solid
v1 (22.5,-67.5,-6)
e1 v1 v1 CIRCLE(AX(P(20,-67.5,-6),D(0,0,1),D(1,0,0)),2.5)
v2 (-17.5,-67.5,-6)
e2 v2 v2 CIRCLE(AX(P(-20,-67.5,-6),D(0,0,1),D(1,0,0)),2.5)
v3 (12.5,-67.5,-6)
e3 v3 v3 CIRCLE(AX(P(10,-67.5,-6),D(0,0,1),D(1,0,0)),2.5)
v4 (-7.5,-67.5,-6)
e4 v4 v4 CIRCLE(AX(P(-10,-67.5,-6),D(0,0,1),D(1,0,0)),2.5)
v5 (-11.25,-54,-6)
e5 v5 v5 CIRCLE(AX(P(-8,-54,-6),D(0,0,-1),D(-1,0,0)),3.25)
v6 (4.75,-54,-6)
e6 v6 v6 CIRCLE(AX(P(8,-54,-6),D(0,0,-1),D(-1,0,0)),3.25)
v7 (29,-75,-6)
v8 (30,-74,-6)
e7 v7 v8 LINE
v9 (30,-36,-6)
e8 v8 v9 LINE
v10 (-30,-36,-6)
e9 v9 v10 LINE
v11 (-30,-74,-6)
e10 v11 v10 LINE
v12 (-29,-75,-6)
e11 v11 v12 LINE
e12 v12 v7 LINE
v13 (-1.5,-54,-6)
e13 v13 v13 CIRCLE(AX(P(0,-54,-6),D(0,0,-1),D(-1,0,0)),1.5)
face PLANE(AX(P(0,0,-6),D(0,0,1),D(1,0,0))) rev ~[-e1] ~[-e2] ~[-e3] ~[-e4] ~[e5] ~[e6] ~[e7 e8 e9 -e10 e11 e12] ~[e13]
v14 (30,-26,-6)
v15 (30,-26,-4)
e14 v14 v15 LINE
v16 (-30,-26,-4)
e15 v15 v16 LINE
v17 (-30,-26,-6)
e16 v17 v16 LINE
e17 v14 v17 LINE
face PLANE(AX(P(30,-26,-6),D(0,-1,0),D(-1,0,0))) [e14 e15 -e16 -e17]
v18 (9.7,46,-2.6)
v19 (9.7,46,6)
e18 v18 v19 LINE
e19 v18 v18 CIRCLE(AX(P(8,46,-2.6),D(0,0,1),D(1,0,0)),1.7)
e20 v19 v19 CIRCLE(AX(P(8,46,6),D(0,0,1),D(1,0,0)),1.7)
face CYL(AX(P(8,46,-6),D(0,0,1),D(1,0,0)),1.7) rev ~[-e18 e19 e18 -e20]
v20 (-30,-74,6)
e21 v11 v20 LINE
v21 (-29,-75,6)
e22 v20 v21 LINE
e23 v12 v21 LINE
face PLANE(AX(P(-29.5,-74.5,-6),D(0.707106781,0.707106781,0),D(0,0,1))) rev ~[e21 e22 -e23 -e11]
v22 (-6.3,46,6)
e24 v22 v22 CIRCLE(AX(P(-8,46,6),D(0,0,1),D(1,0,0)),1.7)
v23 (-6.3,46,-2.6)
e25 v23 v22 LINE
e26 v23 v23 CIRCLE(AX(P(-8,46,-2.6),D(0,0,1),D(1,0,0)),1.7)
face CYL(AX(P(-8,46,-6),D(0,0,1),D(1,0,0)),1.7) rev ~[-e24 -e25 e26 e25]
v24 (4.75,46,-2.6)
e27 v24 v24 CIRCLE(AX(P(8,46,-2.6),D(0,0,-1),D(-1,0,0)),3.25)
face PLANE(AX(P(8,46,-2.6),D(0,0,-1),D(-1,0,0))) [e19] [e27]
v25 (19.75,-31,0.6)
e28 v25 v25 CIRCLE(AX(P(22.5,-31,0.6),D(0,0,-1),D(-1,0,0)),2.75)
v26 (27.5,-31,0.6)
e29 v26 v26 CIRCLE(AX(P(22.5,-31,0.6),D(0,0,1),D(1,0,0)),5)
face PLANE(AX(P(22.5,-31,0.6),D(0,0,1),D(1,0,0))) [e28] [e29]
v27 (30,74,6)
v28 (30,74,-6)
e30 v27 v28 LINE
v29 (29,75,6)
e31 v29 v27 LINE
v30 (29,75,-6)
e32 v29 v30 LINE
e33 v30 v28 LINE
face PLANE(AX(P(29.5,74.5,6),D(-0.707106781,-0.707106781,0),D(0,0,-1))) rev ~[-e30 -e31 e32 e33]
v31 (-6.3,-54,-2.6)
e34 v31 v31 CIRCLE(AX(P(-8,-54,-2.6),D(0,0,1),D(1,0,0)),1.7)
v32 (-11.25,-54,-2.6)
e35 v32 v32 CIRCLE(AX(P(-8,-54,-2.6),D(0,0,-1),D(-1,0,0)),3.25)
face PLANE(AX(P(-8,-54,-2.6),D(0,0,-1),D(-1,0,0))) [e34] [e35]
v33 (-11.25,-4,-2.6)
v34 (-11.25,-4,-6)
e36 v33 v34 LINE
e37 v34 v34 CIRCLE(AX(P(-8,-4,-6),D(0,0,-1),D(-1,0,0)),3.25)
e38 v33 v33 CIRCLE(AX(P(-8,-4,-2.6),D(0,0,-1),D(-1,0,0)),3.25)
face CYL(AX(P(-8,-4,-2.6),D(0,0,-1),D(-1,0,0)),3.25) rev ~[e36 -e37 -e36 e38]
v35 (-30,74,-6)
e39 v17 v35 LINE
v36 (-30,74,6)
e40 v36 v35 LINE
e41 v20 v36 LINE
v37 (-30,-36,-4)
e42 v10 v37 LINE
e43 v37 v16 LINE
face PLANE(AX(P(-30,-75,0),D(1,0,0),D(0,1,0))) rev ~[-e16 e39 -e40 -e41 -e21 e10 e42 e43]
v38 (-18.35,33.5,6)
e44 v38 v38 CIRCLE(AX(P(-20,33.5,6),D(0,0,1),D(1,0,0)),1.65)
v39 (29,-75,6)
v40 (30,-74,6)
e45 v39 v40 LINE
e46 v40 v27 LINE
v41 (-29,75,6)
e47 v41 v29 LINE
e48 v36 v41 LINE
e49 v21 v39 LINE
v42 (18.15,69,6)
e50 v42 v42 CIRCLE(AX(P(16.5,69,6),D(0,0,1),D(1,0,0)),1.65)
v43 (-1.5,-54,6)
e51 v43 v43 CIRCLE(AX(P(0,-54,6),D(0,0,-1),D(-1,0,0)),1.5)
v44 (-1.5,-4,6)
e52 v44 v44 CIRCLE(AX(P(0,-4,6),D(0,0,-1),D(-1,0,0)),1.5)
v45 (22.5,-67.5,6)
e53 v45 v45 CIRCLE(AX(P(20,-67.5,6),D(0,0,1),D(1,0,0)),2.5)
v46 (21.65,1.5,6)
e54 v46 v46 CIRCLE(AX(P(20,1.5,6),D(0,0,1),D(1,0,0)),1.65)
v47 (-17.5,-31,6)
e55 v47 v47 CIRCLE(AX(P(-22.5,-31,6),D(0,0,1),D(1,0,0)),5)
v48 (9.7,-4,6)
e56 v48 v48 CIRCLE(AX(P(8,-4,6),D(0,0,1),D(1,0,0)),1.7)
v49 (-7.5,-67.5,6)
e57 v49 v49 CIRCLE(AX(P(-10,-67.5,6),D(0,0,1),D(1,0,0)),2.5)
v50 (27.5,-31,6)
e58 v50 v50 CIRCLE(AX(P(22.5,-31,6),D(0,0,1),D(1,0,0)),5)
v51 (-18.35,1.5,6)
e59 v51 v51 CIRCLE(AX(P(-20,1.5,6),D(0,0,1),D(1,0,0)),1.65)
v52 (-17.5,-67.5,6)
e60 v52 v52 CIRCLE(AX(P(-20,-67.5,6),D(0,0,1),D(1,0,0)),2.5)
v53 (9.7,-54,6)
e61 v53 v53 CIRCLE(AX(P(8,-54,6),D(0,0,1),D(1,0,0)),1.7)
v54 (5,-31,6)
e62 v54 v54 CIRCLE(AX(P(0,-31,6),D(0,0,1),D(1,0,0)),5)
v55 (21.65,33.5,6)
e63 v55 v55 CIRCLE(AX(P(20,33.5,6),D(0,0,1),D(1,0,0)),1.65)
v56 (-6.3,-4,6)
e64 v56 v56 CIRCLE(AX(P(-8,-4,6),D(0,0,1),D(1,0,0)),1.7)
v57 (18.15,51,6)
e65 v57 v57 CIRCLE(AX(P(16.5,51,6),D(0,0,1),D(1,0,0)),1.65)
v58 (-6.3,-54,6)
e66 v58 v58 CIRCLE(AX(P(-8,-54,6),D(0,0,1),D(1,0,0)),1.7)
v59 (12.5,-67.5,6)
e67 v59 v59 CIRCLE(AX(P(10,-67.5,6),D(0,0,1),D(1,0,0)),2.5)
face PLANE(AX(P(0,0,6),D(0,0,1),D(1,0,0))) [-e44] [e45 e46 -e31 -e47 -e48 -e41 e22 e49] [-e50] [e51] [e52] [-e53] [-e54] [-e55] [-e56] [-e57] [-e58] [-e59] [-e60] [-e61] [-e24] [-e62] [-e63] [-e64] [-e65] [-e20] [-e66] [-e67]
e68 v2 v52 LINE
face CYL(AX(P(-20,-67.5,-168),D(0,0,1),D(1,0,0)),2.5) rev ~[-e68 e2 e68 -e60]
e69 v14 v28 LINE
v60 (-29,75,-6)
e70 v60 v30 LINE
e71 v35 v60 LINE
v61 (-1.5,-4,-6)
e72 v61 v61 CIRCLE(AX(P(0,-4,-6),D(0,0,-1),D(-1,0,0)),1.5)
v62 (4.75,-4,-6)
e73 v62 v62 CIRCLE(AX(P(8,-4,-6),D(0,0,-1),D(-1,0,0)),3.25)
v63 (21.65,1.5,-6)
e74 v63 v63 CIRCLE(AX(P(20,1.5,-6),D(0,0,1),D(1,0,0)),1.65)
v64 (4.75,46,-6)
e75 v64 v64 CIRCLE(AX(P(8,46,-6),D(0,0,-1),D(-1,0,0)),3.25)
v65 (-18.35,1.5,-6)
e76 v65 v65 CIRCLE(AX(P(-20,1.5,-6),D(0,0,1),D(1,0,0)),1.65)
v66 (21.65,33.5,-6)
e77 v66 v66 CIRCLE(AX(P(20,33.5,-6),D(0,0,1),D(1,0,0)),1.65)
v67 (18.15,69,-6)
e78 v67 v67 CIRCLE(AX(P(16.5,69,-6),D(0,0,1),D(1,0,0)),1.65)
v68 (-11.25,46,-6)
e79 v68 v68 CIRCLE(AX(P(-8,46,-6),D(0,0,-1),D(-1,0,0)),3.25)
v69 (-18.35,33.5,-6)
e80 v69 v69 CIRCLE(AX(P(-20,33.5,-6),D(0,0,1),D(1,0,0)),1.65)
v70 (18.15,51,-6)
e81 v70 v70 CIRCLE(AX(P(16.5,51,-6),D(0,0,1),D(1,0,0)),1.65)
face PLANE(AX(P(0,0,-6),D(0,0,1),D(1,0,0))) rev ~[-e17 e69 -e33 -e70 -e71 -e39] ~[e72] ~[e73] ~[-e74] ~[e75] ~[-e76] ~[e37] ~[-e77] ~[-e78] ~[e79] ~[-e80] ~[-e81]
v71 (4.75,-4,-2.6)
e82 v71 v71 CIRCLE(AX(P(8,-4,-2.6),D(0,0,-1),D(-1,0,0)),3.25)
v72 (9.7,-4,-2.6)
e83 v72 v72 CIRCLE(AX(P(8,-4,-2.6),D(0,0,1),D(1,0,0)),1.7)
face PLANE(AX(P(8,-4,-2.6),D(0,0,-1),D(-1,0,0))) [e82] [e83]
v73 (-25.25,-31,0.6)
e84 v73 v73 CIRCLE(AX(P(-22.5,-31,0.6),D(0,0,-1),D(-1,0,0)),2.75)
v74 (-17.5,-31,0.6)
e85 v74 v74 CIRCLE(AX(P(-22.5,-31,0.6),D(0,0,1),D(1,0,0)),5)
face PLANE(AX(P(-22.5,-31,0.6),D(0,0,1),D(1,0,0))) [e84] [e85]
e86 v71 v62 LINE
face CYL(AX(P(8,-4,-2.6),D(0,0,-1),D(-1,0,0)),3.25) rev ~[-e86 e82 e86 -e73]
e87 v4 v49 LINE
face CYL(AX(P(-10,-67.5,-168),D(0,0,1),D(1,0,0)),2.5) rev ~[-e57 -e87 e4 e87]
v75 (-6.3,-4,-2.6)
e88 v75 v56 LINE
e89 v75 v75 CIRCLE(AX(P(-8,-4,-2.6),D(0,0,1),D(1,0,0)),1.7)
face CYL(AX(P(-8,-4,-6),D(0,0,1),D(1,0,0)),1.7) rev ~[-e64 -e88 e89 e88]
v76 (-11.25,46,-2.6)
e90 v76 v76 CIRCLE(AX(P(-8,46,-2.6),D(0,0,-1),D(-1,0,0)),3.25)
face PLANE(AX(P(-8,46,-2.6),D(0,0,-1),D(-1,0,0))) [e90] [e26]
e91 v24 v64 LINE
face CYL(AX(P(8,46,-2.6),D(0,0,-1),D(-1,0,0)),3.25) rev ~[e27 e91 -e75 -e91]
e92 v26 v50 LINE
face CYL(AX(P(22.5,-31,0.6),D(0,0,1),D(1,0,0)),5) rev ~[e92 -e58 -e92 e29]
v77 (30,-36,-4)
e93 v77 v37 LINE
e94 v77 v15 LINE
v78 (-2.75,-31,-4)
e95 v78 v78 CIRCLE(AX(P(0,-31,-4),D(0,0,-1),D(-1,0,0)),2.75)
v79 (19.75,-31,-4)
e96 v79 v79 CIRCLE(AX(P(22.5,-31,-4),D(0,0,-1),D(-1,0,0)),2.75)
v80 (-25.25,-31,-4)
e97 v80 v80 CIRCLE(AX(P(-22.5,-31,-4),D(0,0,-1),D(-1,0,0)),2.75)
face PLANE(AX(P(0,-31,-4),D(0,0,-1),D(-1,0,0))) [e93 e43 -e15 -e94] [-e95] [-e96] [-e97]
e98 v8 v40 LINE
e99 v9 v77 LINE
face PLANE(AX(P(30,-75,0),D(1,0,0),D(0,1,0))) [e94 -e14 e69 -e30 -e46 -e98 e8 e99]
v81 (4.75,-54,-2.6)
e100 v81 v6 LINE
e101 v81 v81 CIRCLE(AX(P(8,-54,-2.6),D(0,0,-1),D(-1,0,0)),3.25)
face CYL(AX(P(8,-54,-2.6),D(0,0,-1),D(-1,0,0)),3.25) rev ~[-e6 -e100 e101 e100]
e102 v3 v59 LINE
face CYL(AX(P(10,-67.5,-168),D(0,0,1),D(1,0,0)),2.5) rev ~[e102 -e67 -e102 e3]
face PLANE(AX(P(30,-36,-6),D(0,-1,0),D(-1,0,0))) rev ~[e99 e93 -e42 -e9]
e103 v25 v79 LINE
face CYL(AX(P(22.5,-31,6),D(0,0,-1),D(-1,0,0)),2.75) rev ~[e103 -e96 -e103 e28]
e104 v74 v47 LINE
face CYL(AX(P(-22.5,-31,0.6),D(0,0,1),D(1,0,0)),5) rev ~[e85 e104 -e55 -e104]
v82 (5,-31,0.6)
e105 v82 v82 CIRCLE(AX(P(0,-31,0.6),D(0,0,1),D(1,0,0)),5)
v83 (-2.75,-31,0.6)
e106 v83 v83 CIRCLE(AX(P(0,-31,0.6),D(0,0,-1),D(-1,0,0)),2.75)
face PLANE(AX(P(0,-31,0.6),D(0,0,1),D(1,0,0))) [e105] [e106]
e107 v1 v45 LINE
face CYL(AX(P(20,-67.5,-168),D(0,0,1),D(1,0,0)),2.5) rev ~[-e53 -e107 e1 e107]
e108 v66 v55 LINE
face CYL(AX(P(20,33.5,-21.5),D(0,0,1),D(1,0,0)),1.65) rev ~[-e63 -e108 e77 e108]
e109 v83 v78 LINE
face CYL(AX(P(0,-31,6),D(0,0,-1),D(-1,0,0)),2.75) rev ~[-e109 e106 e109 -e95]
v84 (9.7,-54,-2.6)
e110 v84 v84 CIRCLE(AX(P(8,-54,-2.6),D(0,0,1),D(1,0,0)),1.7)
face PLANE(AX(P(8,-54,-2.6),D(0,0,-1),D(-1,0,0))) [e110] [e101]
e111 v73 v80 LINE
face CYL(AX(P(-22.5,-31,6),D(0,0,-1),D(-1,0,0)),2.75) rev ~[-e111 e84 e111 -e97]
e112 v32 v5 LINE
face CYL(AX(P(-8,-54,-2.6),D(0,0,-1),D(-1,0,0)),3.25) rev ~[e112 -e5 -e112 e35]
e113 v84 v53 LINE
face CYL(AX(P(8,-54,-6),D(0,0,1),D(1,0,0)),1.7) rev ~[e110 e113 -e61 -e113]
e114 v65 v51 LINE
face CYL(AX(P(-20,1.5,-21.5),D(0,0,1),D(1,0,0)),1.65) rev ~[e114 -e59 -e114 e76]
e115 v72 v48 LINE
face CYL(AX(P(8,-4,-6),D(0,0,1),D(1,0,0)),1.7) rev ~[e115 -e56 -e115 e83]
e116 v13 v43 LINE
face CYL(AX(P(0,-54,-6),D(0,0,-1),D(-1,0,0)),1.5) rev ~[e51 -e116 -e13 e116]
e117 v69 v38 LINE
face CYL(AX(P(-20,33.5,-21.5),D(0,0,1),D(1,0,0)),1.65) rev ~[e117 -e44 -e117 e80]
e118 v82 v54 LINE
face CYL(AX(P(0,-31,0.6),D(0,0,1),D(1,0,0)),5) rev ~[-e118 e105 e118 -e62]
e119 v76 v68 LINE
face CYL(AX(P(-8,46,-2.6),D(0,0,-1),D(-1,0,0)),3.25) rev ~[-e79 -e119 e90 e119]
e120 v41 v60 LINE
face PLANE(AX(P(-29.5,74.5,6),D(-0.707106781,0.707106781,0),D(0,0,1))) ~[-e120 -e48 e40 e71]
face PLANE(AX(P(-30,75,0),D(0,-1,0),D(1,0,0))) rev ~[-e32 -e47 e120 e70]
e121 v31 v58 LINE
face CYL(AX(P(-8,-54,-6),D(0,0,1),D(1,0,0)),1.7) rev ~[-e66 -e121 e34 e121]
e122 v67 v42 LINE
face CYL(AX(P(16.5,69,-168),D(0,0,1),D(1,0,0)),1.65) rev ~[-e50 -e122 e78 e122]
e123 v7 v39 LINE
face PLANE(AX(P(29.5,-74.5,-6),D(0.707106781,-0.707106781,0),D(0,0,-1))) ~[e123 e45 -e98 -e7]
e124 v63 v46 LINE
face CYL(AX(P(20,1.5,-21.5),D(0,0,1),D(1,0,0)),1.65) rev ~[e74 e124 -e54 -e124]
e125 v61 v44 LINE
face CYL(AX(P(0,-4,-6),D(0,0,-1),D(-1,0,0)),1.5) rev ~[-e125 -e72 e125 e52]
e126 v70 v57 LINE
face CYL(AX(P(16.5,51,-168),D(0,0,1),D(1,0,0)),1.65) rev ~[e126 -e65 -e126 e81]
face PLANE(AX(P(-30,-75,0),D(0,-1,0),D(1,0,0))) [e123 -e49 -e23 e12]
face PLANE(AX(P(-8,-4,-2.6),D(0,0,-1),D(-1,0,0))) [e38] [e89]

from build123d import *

# Parameters (mm, degrees)
SKETCH1_W                                           = 60
SKETCH1_H                                           = 150
BOSS_EXTRUDE1_DEPTH                                 = 6
M4_TAPPED_HOLE1_D                                   = 3.3
M4_TAPPED_HOLE2_D                                   = 3.3
M4_TAPPED_HOLE2_DEPTH                               = 15.5
M4_TAPPED_HOLE2_TIP                                 = 0.991420021
M6_TAPPED_HOLE2_D                                   = 5
BLIND_PIN_HOLE2_SIZE_MM_D                           = 5
CHAMFER1_SIZE                                       = 1
CBORE_FOR_M3_HEX_SOCKET_HEAD_CAP_SCREW1_D           = 3.4
CBORE_FOR_M3_HEX_SOCKET_HEAD_CAP_SCREW1_CBORE_D     = 6.5
CBORE_FOR_M3_HEX_SOCKET_HEAD_CAP_SCREW1_CBORE_DEPTH = 3.4
LPATTERN1_COUNT                                     = 3
LPATTERN1_PITCH                                     = 50
SKETCH20_R                                          = 1.5
CUT_EXTRUDE1_DEPTH                                  = 82.663945533
SKETCH21_W                                          = 60
SKETCH21_H                                          = 10
CUT_EXTRUDE2_DEPTH                                  = 2
CBORE_FOR_M5_HEX_SOCKET_HEAD_CAP_SCREW1_D           = 5.5
CBORE_FOR_M5_HEX_SOCKET_HEAD_CAP_SCREW1_CBORE_D     = 10
CBORE_FOR_M5_HEX_SOCKET_HEAD_CAP_SCREW1_CBORE_DEPTH = 5.4


with BuildPart() as part:
    # Sketch1 → Boss-Extrude1 (new, symmetric)
    with BuildSketch(Plane.XY):
        Rectangle(SKETCH1_W, SKETCH1_H)
    extrude(amount=BOSS_EXTRUDE1_DEPTH, both=True)

    # M4 Tapped Hole1 (through all)
    with Locations(Plane(origin=(0, 0, -6), x_dir=(-1, 0, 0), z_dir=(0, 0, -1))):
        with Locations((-16.5, 69), (-16.5, 51)):
            Hole(M4_TAPPED_HOLE1_D / 2)

    # M4 Tapped Hole2
    with Locations(Plane(origin=(0, 0, -6), x_dir=(-1, 0, 0), z_dir=(0, 0, -1))):
        with Locations((-20, 33.5), (-20, 1.5), (20, 33.5), (20, 1.5)):
            Hole(M4_TAPPED_HOLE2_D / 2, depth=M4_TAPPED_HOLE2_DEPTH)
            with Locations((0, 0, -(M4_TAPPED_HOLE2_DEPTH + M4_TAPPED_HOLE2_TIP / 2))):  # 118° drill point
                Cone(0, M4_TAPPED_HOLE2_D / 2, M4_TAPPED_HOLE2_TIP, mode=Mode.SUBTRACT)

    # M6 Tapped Hole2 (through all)
    with Locations(Plane(origin=(0, 0, -6), x_dir=(-1, 0, 0), z_dir=(0, 0, -1))):
        with Locations((20, -67.5), (-20, -67.5)):
            Hole(M6_TAPPED_HOLE2_D / 2)

    # Blind Pin Hole2 size mm (through all)
    with Locations(Plane(origin=(0, 0, -6), x_dir=(-1, 0, 0), z_dir=(0, 0, -1))):
        with Locations((10, -67.5), (-10, -67.5)):
            Hole(BLIND_PIN_HOLE2_SIZE_MM_D / 2)

    # Chamfer1
    chamfer1_edges = [part.edges().sort_by_distance(p)[0] for p in [
        (30, -75, 0),
        (-30, -75, 0),
        (-30, 75, 0),
        (30, 75, 0),
    ]]
    chamfer(chamfer1_edges, length=CHAMFER1_SIZE)

    # CBORE for M3 Hex Socket Head Cap Screw1 (through all)
    with Locations(Plane(origin=(0, 0, -6), x_dir=(-1, 0, 0), z_dir=(0, 0, -1))):
        with Locations((8, -54), (-8, -54)):
            cbore_for_m3_hex_socket_head_cap_screw1 = CounterBoreHole(CBORE_FOR_M3_HEX_SOCKET_HEAD_CAP_SCREW1_D / 2, CBORE_FOR_M3_HEX_SOCKET_HEAD_CAP_SCREW1_CBORE_D / 2, CBORE_FOR_M3_HEX_SOCKET_HEAD_CAP_SCREW1_CBORE_DEPTH)

    # LPattern1: CBORE for M3 Hex Socket Head Cap Screw1 ×3
    with Locations(*[(0, i * LPATTERN1_PITCH, 0) for i in range(1, LPATTERN1_COUNT)]):
        add(cbore_for_m3_hex_socket_head_cap_screw1, mode=Mode.SUBTRACT)

    # Sketch20 → Cut-Extrude1 (cut, through all)
    with BuildSketch(Plane(origin=(0, 0, -6), x_dir=(-1, 0, 0), z_dir=(0, 0, -1))):
        with Locations((0, -4)):
            Circle(SKETCH20_R)
        with Locations((0, -54)):
            Circle(SKETCH20_R)
    extrude(amount=-CUT_EXTRUDE1_DEPTH, mode=Mode.SUBTRACT)

    # Sketch21 → Cut-Extrude2 (cut)
    with BuildSketch(Plane(origin=(0, 0, -6), x_dir=(-1, 0, 0), z_dir=(0, 0, -1))):
        with Locations((0, -31)):
            Rectangle(SKETCH21_W, SKETCH21_H)
    extrude(amount=-CUT_EXTRUDE2_DEPTH, mode=Mode.SUBTRACT)

    # CBORE for M5 Hex Socket Head Cap Screw1 (through all)
    with Locations(Plane.XY.offset(6)):
        with Locations((22.5, -31), (0, -31), (-22.5, -31)):
            CounterBoreHole(CBORE_FOR_M5_HEX_SOCKET_HEAD_CAP_SCREW1_D / 2, CBORE_FOR_M5_HEX_SOCKET_HEAD_CAP_SCREW1_CBORE_D / 2, CBORE_FOR_M5_HEX_SOCKET_HEAD_CAP_SCREW1_CBORE_DEPTH)


solid = part.part
